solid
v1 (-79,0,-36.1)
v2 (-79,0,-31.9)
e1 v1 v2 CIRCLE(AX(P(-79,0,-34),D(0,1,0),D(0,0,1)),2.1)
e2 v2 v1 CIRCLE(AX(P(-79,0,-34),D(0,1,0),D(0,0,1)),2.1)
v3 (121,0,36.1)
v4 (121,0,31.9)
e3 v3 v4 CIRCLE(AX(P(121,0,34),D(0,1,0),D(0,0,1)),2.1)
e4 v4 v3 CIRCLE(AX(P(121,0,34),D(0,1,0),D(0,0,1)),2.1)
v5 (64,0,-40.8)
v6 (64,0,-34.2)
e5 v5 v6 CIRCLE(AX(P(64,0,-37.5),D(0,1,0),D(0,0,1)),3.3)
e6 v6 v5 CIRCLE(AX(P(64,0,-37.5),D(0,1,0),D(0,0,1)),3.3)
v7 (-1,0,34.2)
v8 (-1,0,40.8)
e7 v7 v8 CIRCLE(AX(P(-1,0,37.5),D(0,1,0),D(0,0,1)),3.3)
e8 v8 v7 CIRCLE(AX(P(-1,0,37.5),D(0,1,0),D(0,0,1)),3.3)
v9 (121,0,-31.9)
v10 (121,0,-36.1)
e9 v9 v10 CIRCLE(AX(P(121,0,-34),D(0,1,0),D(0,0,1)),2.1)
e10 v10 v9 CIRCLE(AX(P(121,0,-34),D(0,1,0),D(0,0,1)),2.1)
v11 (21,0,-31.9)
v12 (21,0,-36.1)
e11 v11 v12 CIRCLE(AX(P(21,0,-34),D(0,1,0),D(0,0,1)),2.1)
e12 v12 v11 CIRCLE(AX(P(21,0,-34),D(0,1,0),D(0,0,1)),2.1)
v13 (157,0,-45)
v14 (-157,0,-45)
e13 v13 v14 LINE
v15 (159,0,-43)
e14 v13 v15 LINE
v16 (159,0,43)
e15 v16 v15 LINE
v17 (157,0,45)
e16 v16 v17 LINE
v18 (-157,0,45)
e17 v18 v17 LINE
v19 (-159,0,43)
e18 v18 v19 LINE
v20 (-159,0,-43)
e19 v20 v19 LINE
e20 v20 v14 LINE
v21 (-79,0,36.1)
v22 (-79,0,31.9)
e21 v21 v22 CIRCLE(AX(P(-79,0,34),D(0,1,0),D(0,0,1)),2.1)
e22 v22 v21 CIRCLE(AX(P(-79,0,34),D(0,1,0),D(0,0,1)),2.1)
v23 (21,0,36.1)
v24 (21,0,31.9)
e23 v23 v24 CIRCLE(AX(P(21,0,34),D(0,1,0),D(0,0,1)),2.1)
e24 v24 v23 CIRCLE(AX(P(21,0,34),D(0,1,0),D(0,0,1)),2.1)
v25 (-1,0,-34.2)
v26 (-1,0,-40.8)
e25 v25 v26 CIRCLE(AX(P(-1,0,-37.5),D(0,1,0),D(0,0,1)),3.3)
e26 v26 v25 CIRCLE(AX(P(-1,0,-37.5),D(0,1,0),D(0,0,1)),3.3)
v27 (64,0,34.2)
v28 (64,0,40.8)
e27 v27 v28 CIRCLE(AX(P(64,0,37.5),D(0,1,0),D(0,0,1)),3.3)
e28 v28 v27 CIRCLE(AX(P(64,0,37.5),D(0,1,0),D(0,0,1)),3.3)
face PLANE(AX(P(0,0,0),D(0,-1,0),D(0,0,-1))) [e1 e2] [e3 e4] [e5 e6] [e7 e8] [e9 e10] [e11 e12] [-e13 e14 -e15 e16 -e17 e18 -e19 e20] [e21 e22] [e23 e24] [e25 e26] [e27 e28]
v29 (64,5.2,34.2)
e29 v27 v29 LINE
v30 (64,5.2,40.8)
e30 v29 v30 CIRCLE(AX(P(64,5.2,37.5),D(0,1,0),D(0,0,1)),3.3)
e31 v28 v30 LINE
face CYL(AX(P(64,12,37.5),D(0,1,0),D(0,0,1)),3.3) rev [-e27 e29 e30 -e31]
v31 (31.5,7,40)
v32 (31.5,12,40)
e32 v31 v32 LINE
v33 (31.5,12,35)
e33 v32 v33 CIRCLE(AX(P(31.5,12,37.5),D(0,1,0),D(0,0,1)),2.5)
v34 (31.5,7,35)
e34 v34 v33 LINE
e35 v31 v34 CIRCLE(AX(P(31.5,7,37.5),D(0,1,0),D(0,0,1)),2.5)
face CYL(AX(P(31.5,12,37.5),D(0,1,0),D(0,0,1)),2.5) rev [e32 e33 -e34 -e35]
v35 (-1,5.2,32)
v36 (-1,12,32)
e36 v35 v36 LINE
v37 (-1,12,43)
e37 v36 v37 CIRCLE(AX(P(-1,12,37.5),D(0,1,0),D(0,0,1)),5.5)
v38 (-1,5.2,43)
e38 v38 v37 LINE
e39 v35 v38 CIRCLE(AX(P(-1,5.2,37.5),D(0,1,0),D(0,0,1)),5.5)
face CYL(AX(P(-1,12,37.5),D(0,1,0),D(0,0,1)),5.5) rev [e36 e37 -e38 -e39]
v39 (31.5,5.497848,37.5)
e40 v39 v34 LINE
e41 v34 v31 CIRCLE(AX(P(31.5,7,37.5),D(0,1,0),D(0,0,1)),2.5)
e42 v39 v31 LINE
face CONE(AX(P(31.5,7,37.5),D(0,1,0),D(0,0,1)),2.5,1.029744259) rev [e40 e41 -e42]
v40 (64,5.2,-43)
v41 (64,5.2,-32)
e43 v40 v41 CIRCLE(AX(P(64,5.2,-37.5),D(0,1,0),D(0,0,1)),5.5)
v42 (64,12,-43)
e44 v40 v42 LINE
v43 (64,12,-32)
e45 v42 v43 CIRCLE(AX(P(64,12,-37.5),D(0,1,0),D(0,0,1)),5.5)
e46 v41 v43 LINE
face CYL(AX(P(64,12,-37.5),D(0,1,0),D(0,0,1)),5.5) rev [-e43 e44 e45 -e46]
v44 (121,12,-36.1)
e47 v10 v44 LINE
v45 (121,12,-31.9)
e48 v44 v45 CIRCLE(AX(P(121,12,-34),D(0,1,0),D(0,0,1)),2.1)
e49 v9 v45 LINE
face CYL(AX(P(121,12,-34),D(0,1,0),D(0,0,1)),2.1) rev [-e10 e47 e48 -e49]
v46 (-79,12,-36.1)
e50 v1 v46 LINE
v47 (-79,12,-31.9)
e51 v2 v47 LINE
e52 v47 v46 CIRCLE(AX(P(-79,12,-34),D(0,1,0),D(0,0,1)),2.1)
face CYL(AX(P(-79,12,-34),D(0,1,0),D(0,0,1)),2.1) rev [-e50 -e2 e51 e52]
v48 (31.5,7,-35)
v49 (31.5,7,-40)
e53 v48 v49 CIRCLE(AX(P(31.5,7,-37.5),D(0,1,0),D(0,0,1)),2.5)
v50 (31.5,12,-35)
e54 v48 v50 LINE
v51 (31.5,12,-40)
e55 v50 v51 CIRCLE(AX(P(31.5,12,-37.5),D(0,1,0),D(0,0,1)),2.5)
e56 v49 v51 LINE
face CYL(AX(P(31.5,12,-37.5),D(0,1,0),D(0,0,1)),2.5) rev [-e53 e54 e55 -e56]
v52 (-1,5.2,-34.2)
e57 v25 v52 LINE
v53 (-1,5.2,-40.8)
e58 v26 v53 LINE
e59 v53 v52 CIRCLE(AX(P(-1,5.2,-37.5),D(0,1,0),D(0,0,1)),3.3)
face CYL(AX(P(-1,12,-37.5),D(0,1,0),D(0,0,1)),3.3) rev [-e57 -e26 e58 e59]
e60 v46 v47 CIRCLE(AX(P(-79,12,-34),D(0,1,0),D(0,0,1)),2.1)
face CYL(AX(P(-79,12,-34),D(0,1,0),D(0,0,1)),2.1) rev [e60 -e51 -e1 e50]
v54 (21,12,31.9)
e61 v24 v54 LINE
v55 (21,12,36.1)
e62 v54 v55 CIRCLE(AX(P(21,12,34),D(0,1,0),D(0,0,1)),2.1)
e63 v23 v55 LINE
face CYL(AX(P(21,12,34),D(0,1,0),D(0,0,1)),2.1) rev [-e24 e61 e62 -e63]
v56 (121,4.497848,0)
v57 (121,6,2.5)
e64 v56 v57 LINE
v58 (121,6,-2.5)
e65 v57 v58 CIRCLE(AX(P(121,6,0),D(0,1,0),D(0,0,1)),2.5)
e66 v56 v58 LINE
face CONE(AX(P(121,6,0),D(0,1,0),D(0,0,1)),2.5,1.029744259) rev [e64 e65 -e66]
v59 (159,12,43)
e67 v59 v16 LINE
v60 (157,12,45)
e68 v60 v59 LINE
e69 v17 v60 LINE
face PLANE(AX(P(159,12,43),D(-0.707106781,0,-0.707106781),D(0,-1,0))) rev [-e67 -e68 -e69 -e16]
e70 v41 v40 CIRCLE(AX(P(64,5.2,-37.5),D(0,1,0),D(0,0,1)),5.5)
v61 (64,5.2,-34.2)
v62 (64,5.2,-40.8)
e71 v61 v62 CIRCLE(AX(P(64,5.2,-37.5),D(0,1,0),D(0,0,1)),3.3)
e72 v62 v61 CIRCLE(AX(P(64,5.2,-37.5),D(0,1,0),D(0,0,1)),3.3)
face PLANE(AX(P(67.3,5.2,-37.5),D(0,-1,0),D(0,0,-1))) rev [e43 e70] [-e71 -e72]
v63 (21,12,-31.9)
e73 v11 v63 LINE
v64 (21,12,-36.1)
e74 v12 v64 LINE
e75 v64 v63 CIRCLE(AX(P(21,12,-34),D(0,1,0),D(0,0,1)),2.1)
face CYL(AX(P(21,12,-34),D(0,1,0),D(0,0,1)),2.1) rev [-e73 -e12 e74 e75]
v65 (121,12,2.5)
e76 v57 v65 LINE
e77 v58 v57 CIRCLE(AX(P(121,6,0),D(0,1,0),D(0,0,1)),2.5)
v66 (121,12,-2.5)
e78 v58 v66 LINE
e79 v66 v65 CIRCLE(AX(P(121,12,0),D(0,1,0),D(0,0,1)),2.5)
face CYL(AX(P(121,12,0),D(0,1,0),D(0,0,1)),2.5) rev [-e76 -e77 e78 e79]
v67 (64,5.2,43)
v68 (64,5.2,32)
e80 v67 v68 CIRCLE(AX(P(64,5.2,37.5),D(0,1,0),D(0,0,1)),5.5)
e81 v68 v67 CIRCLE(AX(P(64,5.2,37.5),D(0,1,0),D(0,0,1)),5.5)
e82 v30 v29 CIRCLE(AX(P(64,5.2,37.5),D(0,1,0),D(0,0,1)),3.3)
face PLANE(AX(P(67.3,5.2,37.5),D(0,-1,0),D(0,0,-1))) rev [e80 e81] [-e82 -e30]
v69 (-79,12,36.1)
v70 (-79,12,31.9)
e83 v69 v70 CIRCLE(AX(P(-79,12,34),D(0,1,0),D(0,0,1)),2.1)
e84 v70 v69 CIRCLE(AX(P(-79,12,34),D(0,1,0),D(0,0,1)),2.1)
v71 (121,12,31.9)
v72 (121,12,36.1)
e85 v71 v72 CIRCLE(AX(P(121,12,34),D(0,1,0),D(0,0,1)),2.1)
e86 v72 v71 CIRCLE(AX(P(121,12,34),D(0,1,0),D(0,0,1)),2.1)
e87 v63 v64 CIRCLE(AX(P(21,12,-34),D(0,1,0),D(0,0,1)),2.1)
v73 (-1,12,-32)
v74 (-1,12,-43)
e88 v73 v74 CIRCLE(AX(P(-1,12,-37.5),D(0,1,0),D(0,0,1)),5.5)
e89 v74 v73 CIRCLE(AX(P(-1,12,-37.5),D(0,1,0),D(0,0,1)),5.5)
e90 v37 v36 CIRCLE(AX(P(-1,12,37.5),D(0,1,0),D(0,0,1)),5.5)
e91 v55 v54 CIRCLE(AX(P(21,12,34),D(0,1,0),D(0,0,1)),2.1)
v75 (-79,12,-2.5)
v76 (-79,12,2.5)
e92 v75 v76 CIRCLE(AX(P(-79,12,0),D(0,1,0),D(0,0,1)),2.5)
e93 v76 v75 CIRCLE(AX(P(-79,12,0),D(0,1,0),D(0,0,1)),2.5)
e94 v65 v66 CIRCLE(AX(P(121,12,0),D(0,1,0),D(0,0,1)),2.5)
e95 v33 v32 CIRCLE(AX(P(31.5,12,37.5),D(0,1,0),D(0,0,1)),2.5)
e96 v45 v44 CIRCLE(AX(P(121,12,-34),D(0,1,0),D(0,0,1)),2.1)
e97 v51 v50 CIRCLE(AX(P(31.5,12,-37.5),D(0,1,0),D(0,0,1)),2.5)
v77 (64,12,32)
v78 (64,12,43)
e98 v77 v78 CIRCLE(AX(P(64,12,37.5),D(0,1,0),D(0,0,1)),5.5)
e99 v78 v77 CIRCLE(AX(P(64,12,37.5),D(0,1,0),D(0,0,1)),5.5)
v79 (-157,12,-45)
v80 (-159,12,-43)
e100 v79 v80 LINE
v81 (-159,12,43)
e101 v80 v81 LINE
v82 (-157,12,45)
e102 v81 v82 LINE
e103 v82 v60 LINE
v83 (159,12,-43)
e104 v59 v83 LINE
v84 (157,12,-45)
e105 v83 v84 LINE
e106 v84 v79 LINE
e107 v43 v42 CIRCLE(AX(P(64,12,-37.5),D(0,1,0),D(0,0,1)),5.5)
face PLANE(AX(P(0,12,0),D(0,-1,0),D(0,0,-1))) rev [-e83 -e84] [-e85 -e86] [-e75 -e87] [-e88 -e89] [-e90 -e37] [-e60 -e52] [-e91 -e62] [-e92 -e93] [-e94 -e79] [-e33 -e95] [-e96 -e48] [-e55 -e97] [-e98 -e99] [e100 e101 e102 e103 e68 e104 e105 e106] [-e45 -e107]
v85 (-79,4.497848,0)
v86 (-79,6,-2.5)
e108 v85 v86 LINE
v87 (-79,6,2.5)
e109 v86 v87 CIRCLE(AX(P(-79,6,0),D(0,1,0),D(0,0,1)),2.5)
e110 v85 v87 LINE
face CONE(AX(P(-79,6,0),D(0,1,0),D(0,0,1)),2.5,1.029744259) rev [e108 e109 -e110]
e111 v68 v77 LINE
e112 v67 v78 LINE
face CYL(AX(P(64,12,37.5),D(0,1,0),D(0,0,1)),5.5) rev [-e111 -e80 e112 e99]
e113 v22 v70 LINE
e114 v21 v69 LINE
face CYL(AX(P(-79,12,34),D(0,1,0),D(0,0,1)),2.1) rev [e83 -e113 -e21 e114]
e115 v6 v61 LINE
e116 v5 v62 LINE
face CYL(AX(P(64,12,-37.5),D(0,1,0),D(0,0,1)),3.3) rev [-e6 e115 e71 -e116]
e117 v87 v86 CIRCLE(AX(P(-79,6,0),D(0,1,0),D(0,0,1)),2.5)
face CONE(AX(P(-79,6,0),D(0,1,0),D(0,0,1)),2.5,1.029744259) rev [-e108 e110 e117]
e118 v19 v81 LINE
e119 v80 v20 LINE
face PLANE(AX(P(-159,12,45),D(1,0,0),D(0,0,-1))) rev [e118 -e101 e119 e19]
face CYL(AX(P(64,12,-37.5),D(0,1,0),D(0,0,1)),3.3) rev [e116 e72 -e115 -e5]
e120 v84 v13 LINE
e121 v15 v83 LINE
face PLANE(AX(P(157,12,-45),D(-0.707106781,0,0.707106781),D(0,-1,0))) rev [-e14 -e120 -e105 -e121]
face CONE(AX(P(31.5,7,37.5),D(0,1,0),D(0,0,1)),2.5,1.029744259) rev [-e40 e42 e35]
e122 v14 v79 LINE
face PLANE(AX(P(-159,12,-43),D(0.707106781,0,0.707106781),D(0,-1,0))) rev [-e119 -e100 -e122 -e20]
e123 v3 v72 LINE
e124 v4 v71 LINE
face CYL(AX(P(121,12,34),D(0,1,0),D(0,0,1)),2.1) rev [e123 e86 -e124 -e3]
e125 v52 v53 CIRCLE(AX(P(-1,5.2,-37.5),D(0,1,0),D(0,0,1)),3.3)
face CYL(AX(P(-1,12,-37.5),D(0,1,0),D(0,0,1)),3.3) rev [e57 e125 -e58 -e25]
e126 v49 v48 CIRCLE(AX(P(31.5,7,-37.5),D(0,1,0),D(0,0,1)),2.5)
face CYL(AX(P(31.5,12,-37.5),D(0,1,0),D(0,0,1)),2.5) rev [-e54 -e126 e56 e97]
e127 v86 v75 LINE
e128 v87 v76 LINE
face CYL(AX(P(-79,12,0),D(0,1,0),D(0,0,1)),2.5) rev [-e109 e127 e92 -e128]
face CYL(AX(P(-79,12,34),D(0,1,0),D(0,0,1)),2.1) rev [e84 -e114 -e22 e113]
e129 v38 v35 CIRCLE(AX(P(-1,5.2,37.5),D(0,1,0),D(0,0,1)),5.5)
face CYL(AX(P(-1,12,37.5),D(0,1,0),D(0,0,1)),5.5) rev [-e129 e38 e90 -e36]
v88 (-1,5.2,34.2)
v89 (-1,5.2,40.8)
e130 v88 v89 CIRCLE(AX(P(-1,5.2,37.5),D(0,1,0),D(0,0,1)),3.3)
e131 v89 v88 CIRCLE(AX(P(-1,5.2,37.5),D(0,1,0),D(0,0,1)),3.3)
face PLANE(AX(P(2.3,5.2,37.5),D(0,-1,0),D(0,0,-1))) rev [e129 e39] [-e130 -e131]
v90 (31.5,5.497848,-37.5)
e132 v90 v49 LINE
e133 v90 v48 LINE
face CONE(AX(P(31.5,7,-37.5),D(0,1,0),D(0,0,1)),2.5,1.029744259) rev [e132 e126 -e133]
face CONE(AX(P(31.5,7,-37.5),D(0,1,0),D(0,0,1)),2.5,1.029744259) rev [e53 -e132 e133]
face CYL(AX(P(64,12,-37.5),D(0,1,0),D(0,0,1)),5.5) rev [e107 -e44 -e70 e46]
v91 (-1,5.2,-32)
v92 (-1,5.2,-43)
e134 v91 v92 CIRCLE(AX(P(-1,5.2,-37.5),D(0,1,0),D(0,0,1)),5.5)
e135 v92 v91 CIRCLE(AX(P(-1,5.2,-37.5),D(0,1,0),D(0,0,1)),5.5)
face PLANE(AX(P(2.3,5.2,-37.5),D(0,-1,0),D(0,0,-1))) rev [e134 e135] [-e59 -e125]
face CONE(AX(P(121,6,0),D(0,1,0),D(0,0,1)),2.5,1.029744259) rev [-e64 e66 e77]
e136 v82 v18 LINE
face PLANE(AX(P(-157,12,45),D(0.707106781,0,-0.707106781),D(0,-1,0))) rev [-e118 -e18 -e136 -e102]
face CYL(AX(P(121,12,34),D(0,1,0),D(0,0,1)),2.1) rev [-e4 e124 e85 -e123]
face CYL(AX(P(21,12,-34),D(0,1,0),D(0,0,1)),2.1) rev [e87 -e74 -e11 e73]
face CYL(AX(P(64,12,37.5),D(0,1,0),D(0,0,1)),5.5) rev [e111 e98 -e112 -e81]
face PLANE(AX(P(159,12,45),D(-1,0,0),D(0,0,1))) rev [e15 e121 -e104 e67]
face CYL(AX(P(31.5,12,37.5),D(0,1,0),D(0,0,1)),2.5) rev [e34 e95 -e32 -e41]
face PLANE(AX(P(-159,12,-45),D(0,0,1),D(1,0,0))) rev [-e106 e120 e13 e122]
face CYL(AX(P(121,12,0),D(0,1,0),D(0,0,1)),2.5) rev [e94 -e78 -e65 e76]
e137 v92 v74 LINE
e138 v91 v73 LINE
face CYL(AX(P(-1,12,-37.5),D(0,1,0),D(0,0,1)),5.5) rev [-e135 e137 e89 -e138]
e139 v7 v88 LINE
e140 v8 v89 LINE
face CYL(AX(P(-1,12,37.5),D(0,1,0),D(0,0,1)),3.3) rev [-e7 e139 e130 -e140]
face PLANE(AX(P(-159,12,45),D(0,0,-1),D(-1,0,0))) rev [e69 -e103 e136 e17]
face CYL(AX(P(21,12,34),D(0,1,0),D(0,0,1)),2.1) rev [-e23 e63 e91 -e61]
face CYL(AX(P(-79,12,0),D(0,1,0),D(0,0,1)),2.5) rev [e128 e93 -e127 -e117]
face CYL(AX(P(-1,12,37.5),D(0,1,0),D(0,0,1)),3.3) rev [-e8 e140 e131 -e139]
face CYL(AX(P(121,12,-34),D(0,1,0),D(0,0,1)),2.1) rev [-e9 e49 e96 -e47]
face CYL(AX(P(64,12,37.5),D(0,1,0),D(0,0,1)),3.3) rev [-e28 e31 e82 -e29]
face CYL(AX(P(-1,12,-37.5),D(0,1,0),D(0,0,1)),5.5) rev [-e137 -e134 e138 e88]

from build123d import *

# Parameters (mm, degrees)
SKETCH_1_W                   = 318
SKETCH_1_H                   = 90
EXTRUDE_1_DEPTH              = 12
HOLE_WIZARD_M6_1_D           = 6.6
HOLE_WIZARD_M6_1_CBORE_D     = 11
HOLE_WIZARD_M6_1_CBORE_DEPTH = 6.8
HOLE_WIZARD_M5_1_D           = 4.2
F_5_0MM_1_D                  = 5
F_5_0MM_1_DEPTH              = 6
F_5_0MM_1_TIP                = 1.502151548
F_5_0MM_2_D                  = 5
F_5_0MM_2_DEPTH              = 5
F_5_0MM_2_TIP                = 1.502151548
CHAMFER_1_SIZE               = 2


with BuildPart() as part:
    # 草图1 → 凸台-拉伸1 (new body)
    with BuildSketch(Plane(origin=(0, 0, 0), x_dir=(1, 0, 0), z_dir=(0, 1, 0))):
        Rectangle(SKETCH_1_W, SKETCH_1_H)
    extrude(amount=EXTRUDE_1_DEPTH)

    # M6 六角圆柱头螺钉的柱形沉头孔1 (through all)
    with Locations(Plane(origin=(0, 12, 0), x_dir=(1, 0, 0), z_dir=(0, 1, 0))):
        with Locations((64, 37.5), (-1, 37.5), (-1, -37.5), (64, -37.5)):
            CounterBoreHole(HOLE_WIZARD_M6_1_D / 2, HOLE_WIZARD_M6_1_CBORE_D / 2, HOLE_WIZARD_M6_1_CBORE_DEPTH)

    # M5 螺纹孔1 (through all)
    with Locations(Plane(origin=(0, 12, 0), x_dir=(1, 0, 0), z_dir=(0, 1, 0))):
        with Locations((121, 34), (121, -34), (21, 34), (21, -34), (-79, 34), (-79, -34)):
            Hole(HOLE_WIZARD_M5_1_D / 2)

    # Ø5.0mm 暗销孔1
    with Locations(Plane(origin=(0, 12, 0), x_dir=(1, 0, 0), z_dir=(0, 1, 0))):
        with Locations((121, 0), (-79, 0)):
            Hole(F_5_0MM_1_D / 2, depth=F_5_0MM_1_DEPTH)
            with Locations((0, 0, -(F_5_0MM_1_DEPTH + F_5_0MM_1_TIP / 2))):  # 118° drill point
                Cone(0, F_5_0MM_1_D / 2, F_5_0MM_1_TIP, mode=Mode.SUBTRACT)

    # Ø5.0mm 暗销孔2
    with Locations(Plane(origin=(0, 12, 0), x_dir=(1, 0, 0), z_dir=(0, 1, 0))):
        with Locations((31.5, -37.5), (31.5, 37.5)):
            Hole(F_5_0MM_2_D / 2, depth=F_5_0MM_2_DEPTH)
            with Locations((0, 0, -(F_5_0MM_2_DEPTH + F_5_0MM_2_TIP / 2))):  # 118° drill point
                Cone(0, F_5_0MM_2_D / 2, F_5_0MM_2_TIP, mode=Mode.SUBTRACT)

    # 倒角1
    chamfer_1_edges = [part.edges().sort_by_distance(p)[0] for p in [
        (159, 6, 45),
        (-159, 6, 45),
        (-159, 6, -45),
        (159, 6, -45),
    ]]
    chamfer(chamfer_1_edges, length=CHAMFER_1_SIZE)


solid = part.part
